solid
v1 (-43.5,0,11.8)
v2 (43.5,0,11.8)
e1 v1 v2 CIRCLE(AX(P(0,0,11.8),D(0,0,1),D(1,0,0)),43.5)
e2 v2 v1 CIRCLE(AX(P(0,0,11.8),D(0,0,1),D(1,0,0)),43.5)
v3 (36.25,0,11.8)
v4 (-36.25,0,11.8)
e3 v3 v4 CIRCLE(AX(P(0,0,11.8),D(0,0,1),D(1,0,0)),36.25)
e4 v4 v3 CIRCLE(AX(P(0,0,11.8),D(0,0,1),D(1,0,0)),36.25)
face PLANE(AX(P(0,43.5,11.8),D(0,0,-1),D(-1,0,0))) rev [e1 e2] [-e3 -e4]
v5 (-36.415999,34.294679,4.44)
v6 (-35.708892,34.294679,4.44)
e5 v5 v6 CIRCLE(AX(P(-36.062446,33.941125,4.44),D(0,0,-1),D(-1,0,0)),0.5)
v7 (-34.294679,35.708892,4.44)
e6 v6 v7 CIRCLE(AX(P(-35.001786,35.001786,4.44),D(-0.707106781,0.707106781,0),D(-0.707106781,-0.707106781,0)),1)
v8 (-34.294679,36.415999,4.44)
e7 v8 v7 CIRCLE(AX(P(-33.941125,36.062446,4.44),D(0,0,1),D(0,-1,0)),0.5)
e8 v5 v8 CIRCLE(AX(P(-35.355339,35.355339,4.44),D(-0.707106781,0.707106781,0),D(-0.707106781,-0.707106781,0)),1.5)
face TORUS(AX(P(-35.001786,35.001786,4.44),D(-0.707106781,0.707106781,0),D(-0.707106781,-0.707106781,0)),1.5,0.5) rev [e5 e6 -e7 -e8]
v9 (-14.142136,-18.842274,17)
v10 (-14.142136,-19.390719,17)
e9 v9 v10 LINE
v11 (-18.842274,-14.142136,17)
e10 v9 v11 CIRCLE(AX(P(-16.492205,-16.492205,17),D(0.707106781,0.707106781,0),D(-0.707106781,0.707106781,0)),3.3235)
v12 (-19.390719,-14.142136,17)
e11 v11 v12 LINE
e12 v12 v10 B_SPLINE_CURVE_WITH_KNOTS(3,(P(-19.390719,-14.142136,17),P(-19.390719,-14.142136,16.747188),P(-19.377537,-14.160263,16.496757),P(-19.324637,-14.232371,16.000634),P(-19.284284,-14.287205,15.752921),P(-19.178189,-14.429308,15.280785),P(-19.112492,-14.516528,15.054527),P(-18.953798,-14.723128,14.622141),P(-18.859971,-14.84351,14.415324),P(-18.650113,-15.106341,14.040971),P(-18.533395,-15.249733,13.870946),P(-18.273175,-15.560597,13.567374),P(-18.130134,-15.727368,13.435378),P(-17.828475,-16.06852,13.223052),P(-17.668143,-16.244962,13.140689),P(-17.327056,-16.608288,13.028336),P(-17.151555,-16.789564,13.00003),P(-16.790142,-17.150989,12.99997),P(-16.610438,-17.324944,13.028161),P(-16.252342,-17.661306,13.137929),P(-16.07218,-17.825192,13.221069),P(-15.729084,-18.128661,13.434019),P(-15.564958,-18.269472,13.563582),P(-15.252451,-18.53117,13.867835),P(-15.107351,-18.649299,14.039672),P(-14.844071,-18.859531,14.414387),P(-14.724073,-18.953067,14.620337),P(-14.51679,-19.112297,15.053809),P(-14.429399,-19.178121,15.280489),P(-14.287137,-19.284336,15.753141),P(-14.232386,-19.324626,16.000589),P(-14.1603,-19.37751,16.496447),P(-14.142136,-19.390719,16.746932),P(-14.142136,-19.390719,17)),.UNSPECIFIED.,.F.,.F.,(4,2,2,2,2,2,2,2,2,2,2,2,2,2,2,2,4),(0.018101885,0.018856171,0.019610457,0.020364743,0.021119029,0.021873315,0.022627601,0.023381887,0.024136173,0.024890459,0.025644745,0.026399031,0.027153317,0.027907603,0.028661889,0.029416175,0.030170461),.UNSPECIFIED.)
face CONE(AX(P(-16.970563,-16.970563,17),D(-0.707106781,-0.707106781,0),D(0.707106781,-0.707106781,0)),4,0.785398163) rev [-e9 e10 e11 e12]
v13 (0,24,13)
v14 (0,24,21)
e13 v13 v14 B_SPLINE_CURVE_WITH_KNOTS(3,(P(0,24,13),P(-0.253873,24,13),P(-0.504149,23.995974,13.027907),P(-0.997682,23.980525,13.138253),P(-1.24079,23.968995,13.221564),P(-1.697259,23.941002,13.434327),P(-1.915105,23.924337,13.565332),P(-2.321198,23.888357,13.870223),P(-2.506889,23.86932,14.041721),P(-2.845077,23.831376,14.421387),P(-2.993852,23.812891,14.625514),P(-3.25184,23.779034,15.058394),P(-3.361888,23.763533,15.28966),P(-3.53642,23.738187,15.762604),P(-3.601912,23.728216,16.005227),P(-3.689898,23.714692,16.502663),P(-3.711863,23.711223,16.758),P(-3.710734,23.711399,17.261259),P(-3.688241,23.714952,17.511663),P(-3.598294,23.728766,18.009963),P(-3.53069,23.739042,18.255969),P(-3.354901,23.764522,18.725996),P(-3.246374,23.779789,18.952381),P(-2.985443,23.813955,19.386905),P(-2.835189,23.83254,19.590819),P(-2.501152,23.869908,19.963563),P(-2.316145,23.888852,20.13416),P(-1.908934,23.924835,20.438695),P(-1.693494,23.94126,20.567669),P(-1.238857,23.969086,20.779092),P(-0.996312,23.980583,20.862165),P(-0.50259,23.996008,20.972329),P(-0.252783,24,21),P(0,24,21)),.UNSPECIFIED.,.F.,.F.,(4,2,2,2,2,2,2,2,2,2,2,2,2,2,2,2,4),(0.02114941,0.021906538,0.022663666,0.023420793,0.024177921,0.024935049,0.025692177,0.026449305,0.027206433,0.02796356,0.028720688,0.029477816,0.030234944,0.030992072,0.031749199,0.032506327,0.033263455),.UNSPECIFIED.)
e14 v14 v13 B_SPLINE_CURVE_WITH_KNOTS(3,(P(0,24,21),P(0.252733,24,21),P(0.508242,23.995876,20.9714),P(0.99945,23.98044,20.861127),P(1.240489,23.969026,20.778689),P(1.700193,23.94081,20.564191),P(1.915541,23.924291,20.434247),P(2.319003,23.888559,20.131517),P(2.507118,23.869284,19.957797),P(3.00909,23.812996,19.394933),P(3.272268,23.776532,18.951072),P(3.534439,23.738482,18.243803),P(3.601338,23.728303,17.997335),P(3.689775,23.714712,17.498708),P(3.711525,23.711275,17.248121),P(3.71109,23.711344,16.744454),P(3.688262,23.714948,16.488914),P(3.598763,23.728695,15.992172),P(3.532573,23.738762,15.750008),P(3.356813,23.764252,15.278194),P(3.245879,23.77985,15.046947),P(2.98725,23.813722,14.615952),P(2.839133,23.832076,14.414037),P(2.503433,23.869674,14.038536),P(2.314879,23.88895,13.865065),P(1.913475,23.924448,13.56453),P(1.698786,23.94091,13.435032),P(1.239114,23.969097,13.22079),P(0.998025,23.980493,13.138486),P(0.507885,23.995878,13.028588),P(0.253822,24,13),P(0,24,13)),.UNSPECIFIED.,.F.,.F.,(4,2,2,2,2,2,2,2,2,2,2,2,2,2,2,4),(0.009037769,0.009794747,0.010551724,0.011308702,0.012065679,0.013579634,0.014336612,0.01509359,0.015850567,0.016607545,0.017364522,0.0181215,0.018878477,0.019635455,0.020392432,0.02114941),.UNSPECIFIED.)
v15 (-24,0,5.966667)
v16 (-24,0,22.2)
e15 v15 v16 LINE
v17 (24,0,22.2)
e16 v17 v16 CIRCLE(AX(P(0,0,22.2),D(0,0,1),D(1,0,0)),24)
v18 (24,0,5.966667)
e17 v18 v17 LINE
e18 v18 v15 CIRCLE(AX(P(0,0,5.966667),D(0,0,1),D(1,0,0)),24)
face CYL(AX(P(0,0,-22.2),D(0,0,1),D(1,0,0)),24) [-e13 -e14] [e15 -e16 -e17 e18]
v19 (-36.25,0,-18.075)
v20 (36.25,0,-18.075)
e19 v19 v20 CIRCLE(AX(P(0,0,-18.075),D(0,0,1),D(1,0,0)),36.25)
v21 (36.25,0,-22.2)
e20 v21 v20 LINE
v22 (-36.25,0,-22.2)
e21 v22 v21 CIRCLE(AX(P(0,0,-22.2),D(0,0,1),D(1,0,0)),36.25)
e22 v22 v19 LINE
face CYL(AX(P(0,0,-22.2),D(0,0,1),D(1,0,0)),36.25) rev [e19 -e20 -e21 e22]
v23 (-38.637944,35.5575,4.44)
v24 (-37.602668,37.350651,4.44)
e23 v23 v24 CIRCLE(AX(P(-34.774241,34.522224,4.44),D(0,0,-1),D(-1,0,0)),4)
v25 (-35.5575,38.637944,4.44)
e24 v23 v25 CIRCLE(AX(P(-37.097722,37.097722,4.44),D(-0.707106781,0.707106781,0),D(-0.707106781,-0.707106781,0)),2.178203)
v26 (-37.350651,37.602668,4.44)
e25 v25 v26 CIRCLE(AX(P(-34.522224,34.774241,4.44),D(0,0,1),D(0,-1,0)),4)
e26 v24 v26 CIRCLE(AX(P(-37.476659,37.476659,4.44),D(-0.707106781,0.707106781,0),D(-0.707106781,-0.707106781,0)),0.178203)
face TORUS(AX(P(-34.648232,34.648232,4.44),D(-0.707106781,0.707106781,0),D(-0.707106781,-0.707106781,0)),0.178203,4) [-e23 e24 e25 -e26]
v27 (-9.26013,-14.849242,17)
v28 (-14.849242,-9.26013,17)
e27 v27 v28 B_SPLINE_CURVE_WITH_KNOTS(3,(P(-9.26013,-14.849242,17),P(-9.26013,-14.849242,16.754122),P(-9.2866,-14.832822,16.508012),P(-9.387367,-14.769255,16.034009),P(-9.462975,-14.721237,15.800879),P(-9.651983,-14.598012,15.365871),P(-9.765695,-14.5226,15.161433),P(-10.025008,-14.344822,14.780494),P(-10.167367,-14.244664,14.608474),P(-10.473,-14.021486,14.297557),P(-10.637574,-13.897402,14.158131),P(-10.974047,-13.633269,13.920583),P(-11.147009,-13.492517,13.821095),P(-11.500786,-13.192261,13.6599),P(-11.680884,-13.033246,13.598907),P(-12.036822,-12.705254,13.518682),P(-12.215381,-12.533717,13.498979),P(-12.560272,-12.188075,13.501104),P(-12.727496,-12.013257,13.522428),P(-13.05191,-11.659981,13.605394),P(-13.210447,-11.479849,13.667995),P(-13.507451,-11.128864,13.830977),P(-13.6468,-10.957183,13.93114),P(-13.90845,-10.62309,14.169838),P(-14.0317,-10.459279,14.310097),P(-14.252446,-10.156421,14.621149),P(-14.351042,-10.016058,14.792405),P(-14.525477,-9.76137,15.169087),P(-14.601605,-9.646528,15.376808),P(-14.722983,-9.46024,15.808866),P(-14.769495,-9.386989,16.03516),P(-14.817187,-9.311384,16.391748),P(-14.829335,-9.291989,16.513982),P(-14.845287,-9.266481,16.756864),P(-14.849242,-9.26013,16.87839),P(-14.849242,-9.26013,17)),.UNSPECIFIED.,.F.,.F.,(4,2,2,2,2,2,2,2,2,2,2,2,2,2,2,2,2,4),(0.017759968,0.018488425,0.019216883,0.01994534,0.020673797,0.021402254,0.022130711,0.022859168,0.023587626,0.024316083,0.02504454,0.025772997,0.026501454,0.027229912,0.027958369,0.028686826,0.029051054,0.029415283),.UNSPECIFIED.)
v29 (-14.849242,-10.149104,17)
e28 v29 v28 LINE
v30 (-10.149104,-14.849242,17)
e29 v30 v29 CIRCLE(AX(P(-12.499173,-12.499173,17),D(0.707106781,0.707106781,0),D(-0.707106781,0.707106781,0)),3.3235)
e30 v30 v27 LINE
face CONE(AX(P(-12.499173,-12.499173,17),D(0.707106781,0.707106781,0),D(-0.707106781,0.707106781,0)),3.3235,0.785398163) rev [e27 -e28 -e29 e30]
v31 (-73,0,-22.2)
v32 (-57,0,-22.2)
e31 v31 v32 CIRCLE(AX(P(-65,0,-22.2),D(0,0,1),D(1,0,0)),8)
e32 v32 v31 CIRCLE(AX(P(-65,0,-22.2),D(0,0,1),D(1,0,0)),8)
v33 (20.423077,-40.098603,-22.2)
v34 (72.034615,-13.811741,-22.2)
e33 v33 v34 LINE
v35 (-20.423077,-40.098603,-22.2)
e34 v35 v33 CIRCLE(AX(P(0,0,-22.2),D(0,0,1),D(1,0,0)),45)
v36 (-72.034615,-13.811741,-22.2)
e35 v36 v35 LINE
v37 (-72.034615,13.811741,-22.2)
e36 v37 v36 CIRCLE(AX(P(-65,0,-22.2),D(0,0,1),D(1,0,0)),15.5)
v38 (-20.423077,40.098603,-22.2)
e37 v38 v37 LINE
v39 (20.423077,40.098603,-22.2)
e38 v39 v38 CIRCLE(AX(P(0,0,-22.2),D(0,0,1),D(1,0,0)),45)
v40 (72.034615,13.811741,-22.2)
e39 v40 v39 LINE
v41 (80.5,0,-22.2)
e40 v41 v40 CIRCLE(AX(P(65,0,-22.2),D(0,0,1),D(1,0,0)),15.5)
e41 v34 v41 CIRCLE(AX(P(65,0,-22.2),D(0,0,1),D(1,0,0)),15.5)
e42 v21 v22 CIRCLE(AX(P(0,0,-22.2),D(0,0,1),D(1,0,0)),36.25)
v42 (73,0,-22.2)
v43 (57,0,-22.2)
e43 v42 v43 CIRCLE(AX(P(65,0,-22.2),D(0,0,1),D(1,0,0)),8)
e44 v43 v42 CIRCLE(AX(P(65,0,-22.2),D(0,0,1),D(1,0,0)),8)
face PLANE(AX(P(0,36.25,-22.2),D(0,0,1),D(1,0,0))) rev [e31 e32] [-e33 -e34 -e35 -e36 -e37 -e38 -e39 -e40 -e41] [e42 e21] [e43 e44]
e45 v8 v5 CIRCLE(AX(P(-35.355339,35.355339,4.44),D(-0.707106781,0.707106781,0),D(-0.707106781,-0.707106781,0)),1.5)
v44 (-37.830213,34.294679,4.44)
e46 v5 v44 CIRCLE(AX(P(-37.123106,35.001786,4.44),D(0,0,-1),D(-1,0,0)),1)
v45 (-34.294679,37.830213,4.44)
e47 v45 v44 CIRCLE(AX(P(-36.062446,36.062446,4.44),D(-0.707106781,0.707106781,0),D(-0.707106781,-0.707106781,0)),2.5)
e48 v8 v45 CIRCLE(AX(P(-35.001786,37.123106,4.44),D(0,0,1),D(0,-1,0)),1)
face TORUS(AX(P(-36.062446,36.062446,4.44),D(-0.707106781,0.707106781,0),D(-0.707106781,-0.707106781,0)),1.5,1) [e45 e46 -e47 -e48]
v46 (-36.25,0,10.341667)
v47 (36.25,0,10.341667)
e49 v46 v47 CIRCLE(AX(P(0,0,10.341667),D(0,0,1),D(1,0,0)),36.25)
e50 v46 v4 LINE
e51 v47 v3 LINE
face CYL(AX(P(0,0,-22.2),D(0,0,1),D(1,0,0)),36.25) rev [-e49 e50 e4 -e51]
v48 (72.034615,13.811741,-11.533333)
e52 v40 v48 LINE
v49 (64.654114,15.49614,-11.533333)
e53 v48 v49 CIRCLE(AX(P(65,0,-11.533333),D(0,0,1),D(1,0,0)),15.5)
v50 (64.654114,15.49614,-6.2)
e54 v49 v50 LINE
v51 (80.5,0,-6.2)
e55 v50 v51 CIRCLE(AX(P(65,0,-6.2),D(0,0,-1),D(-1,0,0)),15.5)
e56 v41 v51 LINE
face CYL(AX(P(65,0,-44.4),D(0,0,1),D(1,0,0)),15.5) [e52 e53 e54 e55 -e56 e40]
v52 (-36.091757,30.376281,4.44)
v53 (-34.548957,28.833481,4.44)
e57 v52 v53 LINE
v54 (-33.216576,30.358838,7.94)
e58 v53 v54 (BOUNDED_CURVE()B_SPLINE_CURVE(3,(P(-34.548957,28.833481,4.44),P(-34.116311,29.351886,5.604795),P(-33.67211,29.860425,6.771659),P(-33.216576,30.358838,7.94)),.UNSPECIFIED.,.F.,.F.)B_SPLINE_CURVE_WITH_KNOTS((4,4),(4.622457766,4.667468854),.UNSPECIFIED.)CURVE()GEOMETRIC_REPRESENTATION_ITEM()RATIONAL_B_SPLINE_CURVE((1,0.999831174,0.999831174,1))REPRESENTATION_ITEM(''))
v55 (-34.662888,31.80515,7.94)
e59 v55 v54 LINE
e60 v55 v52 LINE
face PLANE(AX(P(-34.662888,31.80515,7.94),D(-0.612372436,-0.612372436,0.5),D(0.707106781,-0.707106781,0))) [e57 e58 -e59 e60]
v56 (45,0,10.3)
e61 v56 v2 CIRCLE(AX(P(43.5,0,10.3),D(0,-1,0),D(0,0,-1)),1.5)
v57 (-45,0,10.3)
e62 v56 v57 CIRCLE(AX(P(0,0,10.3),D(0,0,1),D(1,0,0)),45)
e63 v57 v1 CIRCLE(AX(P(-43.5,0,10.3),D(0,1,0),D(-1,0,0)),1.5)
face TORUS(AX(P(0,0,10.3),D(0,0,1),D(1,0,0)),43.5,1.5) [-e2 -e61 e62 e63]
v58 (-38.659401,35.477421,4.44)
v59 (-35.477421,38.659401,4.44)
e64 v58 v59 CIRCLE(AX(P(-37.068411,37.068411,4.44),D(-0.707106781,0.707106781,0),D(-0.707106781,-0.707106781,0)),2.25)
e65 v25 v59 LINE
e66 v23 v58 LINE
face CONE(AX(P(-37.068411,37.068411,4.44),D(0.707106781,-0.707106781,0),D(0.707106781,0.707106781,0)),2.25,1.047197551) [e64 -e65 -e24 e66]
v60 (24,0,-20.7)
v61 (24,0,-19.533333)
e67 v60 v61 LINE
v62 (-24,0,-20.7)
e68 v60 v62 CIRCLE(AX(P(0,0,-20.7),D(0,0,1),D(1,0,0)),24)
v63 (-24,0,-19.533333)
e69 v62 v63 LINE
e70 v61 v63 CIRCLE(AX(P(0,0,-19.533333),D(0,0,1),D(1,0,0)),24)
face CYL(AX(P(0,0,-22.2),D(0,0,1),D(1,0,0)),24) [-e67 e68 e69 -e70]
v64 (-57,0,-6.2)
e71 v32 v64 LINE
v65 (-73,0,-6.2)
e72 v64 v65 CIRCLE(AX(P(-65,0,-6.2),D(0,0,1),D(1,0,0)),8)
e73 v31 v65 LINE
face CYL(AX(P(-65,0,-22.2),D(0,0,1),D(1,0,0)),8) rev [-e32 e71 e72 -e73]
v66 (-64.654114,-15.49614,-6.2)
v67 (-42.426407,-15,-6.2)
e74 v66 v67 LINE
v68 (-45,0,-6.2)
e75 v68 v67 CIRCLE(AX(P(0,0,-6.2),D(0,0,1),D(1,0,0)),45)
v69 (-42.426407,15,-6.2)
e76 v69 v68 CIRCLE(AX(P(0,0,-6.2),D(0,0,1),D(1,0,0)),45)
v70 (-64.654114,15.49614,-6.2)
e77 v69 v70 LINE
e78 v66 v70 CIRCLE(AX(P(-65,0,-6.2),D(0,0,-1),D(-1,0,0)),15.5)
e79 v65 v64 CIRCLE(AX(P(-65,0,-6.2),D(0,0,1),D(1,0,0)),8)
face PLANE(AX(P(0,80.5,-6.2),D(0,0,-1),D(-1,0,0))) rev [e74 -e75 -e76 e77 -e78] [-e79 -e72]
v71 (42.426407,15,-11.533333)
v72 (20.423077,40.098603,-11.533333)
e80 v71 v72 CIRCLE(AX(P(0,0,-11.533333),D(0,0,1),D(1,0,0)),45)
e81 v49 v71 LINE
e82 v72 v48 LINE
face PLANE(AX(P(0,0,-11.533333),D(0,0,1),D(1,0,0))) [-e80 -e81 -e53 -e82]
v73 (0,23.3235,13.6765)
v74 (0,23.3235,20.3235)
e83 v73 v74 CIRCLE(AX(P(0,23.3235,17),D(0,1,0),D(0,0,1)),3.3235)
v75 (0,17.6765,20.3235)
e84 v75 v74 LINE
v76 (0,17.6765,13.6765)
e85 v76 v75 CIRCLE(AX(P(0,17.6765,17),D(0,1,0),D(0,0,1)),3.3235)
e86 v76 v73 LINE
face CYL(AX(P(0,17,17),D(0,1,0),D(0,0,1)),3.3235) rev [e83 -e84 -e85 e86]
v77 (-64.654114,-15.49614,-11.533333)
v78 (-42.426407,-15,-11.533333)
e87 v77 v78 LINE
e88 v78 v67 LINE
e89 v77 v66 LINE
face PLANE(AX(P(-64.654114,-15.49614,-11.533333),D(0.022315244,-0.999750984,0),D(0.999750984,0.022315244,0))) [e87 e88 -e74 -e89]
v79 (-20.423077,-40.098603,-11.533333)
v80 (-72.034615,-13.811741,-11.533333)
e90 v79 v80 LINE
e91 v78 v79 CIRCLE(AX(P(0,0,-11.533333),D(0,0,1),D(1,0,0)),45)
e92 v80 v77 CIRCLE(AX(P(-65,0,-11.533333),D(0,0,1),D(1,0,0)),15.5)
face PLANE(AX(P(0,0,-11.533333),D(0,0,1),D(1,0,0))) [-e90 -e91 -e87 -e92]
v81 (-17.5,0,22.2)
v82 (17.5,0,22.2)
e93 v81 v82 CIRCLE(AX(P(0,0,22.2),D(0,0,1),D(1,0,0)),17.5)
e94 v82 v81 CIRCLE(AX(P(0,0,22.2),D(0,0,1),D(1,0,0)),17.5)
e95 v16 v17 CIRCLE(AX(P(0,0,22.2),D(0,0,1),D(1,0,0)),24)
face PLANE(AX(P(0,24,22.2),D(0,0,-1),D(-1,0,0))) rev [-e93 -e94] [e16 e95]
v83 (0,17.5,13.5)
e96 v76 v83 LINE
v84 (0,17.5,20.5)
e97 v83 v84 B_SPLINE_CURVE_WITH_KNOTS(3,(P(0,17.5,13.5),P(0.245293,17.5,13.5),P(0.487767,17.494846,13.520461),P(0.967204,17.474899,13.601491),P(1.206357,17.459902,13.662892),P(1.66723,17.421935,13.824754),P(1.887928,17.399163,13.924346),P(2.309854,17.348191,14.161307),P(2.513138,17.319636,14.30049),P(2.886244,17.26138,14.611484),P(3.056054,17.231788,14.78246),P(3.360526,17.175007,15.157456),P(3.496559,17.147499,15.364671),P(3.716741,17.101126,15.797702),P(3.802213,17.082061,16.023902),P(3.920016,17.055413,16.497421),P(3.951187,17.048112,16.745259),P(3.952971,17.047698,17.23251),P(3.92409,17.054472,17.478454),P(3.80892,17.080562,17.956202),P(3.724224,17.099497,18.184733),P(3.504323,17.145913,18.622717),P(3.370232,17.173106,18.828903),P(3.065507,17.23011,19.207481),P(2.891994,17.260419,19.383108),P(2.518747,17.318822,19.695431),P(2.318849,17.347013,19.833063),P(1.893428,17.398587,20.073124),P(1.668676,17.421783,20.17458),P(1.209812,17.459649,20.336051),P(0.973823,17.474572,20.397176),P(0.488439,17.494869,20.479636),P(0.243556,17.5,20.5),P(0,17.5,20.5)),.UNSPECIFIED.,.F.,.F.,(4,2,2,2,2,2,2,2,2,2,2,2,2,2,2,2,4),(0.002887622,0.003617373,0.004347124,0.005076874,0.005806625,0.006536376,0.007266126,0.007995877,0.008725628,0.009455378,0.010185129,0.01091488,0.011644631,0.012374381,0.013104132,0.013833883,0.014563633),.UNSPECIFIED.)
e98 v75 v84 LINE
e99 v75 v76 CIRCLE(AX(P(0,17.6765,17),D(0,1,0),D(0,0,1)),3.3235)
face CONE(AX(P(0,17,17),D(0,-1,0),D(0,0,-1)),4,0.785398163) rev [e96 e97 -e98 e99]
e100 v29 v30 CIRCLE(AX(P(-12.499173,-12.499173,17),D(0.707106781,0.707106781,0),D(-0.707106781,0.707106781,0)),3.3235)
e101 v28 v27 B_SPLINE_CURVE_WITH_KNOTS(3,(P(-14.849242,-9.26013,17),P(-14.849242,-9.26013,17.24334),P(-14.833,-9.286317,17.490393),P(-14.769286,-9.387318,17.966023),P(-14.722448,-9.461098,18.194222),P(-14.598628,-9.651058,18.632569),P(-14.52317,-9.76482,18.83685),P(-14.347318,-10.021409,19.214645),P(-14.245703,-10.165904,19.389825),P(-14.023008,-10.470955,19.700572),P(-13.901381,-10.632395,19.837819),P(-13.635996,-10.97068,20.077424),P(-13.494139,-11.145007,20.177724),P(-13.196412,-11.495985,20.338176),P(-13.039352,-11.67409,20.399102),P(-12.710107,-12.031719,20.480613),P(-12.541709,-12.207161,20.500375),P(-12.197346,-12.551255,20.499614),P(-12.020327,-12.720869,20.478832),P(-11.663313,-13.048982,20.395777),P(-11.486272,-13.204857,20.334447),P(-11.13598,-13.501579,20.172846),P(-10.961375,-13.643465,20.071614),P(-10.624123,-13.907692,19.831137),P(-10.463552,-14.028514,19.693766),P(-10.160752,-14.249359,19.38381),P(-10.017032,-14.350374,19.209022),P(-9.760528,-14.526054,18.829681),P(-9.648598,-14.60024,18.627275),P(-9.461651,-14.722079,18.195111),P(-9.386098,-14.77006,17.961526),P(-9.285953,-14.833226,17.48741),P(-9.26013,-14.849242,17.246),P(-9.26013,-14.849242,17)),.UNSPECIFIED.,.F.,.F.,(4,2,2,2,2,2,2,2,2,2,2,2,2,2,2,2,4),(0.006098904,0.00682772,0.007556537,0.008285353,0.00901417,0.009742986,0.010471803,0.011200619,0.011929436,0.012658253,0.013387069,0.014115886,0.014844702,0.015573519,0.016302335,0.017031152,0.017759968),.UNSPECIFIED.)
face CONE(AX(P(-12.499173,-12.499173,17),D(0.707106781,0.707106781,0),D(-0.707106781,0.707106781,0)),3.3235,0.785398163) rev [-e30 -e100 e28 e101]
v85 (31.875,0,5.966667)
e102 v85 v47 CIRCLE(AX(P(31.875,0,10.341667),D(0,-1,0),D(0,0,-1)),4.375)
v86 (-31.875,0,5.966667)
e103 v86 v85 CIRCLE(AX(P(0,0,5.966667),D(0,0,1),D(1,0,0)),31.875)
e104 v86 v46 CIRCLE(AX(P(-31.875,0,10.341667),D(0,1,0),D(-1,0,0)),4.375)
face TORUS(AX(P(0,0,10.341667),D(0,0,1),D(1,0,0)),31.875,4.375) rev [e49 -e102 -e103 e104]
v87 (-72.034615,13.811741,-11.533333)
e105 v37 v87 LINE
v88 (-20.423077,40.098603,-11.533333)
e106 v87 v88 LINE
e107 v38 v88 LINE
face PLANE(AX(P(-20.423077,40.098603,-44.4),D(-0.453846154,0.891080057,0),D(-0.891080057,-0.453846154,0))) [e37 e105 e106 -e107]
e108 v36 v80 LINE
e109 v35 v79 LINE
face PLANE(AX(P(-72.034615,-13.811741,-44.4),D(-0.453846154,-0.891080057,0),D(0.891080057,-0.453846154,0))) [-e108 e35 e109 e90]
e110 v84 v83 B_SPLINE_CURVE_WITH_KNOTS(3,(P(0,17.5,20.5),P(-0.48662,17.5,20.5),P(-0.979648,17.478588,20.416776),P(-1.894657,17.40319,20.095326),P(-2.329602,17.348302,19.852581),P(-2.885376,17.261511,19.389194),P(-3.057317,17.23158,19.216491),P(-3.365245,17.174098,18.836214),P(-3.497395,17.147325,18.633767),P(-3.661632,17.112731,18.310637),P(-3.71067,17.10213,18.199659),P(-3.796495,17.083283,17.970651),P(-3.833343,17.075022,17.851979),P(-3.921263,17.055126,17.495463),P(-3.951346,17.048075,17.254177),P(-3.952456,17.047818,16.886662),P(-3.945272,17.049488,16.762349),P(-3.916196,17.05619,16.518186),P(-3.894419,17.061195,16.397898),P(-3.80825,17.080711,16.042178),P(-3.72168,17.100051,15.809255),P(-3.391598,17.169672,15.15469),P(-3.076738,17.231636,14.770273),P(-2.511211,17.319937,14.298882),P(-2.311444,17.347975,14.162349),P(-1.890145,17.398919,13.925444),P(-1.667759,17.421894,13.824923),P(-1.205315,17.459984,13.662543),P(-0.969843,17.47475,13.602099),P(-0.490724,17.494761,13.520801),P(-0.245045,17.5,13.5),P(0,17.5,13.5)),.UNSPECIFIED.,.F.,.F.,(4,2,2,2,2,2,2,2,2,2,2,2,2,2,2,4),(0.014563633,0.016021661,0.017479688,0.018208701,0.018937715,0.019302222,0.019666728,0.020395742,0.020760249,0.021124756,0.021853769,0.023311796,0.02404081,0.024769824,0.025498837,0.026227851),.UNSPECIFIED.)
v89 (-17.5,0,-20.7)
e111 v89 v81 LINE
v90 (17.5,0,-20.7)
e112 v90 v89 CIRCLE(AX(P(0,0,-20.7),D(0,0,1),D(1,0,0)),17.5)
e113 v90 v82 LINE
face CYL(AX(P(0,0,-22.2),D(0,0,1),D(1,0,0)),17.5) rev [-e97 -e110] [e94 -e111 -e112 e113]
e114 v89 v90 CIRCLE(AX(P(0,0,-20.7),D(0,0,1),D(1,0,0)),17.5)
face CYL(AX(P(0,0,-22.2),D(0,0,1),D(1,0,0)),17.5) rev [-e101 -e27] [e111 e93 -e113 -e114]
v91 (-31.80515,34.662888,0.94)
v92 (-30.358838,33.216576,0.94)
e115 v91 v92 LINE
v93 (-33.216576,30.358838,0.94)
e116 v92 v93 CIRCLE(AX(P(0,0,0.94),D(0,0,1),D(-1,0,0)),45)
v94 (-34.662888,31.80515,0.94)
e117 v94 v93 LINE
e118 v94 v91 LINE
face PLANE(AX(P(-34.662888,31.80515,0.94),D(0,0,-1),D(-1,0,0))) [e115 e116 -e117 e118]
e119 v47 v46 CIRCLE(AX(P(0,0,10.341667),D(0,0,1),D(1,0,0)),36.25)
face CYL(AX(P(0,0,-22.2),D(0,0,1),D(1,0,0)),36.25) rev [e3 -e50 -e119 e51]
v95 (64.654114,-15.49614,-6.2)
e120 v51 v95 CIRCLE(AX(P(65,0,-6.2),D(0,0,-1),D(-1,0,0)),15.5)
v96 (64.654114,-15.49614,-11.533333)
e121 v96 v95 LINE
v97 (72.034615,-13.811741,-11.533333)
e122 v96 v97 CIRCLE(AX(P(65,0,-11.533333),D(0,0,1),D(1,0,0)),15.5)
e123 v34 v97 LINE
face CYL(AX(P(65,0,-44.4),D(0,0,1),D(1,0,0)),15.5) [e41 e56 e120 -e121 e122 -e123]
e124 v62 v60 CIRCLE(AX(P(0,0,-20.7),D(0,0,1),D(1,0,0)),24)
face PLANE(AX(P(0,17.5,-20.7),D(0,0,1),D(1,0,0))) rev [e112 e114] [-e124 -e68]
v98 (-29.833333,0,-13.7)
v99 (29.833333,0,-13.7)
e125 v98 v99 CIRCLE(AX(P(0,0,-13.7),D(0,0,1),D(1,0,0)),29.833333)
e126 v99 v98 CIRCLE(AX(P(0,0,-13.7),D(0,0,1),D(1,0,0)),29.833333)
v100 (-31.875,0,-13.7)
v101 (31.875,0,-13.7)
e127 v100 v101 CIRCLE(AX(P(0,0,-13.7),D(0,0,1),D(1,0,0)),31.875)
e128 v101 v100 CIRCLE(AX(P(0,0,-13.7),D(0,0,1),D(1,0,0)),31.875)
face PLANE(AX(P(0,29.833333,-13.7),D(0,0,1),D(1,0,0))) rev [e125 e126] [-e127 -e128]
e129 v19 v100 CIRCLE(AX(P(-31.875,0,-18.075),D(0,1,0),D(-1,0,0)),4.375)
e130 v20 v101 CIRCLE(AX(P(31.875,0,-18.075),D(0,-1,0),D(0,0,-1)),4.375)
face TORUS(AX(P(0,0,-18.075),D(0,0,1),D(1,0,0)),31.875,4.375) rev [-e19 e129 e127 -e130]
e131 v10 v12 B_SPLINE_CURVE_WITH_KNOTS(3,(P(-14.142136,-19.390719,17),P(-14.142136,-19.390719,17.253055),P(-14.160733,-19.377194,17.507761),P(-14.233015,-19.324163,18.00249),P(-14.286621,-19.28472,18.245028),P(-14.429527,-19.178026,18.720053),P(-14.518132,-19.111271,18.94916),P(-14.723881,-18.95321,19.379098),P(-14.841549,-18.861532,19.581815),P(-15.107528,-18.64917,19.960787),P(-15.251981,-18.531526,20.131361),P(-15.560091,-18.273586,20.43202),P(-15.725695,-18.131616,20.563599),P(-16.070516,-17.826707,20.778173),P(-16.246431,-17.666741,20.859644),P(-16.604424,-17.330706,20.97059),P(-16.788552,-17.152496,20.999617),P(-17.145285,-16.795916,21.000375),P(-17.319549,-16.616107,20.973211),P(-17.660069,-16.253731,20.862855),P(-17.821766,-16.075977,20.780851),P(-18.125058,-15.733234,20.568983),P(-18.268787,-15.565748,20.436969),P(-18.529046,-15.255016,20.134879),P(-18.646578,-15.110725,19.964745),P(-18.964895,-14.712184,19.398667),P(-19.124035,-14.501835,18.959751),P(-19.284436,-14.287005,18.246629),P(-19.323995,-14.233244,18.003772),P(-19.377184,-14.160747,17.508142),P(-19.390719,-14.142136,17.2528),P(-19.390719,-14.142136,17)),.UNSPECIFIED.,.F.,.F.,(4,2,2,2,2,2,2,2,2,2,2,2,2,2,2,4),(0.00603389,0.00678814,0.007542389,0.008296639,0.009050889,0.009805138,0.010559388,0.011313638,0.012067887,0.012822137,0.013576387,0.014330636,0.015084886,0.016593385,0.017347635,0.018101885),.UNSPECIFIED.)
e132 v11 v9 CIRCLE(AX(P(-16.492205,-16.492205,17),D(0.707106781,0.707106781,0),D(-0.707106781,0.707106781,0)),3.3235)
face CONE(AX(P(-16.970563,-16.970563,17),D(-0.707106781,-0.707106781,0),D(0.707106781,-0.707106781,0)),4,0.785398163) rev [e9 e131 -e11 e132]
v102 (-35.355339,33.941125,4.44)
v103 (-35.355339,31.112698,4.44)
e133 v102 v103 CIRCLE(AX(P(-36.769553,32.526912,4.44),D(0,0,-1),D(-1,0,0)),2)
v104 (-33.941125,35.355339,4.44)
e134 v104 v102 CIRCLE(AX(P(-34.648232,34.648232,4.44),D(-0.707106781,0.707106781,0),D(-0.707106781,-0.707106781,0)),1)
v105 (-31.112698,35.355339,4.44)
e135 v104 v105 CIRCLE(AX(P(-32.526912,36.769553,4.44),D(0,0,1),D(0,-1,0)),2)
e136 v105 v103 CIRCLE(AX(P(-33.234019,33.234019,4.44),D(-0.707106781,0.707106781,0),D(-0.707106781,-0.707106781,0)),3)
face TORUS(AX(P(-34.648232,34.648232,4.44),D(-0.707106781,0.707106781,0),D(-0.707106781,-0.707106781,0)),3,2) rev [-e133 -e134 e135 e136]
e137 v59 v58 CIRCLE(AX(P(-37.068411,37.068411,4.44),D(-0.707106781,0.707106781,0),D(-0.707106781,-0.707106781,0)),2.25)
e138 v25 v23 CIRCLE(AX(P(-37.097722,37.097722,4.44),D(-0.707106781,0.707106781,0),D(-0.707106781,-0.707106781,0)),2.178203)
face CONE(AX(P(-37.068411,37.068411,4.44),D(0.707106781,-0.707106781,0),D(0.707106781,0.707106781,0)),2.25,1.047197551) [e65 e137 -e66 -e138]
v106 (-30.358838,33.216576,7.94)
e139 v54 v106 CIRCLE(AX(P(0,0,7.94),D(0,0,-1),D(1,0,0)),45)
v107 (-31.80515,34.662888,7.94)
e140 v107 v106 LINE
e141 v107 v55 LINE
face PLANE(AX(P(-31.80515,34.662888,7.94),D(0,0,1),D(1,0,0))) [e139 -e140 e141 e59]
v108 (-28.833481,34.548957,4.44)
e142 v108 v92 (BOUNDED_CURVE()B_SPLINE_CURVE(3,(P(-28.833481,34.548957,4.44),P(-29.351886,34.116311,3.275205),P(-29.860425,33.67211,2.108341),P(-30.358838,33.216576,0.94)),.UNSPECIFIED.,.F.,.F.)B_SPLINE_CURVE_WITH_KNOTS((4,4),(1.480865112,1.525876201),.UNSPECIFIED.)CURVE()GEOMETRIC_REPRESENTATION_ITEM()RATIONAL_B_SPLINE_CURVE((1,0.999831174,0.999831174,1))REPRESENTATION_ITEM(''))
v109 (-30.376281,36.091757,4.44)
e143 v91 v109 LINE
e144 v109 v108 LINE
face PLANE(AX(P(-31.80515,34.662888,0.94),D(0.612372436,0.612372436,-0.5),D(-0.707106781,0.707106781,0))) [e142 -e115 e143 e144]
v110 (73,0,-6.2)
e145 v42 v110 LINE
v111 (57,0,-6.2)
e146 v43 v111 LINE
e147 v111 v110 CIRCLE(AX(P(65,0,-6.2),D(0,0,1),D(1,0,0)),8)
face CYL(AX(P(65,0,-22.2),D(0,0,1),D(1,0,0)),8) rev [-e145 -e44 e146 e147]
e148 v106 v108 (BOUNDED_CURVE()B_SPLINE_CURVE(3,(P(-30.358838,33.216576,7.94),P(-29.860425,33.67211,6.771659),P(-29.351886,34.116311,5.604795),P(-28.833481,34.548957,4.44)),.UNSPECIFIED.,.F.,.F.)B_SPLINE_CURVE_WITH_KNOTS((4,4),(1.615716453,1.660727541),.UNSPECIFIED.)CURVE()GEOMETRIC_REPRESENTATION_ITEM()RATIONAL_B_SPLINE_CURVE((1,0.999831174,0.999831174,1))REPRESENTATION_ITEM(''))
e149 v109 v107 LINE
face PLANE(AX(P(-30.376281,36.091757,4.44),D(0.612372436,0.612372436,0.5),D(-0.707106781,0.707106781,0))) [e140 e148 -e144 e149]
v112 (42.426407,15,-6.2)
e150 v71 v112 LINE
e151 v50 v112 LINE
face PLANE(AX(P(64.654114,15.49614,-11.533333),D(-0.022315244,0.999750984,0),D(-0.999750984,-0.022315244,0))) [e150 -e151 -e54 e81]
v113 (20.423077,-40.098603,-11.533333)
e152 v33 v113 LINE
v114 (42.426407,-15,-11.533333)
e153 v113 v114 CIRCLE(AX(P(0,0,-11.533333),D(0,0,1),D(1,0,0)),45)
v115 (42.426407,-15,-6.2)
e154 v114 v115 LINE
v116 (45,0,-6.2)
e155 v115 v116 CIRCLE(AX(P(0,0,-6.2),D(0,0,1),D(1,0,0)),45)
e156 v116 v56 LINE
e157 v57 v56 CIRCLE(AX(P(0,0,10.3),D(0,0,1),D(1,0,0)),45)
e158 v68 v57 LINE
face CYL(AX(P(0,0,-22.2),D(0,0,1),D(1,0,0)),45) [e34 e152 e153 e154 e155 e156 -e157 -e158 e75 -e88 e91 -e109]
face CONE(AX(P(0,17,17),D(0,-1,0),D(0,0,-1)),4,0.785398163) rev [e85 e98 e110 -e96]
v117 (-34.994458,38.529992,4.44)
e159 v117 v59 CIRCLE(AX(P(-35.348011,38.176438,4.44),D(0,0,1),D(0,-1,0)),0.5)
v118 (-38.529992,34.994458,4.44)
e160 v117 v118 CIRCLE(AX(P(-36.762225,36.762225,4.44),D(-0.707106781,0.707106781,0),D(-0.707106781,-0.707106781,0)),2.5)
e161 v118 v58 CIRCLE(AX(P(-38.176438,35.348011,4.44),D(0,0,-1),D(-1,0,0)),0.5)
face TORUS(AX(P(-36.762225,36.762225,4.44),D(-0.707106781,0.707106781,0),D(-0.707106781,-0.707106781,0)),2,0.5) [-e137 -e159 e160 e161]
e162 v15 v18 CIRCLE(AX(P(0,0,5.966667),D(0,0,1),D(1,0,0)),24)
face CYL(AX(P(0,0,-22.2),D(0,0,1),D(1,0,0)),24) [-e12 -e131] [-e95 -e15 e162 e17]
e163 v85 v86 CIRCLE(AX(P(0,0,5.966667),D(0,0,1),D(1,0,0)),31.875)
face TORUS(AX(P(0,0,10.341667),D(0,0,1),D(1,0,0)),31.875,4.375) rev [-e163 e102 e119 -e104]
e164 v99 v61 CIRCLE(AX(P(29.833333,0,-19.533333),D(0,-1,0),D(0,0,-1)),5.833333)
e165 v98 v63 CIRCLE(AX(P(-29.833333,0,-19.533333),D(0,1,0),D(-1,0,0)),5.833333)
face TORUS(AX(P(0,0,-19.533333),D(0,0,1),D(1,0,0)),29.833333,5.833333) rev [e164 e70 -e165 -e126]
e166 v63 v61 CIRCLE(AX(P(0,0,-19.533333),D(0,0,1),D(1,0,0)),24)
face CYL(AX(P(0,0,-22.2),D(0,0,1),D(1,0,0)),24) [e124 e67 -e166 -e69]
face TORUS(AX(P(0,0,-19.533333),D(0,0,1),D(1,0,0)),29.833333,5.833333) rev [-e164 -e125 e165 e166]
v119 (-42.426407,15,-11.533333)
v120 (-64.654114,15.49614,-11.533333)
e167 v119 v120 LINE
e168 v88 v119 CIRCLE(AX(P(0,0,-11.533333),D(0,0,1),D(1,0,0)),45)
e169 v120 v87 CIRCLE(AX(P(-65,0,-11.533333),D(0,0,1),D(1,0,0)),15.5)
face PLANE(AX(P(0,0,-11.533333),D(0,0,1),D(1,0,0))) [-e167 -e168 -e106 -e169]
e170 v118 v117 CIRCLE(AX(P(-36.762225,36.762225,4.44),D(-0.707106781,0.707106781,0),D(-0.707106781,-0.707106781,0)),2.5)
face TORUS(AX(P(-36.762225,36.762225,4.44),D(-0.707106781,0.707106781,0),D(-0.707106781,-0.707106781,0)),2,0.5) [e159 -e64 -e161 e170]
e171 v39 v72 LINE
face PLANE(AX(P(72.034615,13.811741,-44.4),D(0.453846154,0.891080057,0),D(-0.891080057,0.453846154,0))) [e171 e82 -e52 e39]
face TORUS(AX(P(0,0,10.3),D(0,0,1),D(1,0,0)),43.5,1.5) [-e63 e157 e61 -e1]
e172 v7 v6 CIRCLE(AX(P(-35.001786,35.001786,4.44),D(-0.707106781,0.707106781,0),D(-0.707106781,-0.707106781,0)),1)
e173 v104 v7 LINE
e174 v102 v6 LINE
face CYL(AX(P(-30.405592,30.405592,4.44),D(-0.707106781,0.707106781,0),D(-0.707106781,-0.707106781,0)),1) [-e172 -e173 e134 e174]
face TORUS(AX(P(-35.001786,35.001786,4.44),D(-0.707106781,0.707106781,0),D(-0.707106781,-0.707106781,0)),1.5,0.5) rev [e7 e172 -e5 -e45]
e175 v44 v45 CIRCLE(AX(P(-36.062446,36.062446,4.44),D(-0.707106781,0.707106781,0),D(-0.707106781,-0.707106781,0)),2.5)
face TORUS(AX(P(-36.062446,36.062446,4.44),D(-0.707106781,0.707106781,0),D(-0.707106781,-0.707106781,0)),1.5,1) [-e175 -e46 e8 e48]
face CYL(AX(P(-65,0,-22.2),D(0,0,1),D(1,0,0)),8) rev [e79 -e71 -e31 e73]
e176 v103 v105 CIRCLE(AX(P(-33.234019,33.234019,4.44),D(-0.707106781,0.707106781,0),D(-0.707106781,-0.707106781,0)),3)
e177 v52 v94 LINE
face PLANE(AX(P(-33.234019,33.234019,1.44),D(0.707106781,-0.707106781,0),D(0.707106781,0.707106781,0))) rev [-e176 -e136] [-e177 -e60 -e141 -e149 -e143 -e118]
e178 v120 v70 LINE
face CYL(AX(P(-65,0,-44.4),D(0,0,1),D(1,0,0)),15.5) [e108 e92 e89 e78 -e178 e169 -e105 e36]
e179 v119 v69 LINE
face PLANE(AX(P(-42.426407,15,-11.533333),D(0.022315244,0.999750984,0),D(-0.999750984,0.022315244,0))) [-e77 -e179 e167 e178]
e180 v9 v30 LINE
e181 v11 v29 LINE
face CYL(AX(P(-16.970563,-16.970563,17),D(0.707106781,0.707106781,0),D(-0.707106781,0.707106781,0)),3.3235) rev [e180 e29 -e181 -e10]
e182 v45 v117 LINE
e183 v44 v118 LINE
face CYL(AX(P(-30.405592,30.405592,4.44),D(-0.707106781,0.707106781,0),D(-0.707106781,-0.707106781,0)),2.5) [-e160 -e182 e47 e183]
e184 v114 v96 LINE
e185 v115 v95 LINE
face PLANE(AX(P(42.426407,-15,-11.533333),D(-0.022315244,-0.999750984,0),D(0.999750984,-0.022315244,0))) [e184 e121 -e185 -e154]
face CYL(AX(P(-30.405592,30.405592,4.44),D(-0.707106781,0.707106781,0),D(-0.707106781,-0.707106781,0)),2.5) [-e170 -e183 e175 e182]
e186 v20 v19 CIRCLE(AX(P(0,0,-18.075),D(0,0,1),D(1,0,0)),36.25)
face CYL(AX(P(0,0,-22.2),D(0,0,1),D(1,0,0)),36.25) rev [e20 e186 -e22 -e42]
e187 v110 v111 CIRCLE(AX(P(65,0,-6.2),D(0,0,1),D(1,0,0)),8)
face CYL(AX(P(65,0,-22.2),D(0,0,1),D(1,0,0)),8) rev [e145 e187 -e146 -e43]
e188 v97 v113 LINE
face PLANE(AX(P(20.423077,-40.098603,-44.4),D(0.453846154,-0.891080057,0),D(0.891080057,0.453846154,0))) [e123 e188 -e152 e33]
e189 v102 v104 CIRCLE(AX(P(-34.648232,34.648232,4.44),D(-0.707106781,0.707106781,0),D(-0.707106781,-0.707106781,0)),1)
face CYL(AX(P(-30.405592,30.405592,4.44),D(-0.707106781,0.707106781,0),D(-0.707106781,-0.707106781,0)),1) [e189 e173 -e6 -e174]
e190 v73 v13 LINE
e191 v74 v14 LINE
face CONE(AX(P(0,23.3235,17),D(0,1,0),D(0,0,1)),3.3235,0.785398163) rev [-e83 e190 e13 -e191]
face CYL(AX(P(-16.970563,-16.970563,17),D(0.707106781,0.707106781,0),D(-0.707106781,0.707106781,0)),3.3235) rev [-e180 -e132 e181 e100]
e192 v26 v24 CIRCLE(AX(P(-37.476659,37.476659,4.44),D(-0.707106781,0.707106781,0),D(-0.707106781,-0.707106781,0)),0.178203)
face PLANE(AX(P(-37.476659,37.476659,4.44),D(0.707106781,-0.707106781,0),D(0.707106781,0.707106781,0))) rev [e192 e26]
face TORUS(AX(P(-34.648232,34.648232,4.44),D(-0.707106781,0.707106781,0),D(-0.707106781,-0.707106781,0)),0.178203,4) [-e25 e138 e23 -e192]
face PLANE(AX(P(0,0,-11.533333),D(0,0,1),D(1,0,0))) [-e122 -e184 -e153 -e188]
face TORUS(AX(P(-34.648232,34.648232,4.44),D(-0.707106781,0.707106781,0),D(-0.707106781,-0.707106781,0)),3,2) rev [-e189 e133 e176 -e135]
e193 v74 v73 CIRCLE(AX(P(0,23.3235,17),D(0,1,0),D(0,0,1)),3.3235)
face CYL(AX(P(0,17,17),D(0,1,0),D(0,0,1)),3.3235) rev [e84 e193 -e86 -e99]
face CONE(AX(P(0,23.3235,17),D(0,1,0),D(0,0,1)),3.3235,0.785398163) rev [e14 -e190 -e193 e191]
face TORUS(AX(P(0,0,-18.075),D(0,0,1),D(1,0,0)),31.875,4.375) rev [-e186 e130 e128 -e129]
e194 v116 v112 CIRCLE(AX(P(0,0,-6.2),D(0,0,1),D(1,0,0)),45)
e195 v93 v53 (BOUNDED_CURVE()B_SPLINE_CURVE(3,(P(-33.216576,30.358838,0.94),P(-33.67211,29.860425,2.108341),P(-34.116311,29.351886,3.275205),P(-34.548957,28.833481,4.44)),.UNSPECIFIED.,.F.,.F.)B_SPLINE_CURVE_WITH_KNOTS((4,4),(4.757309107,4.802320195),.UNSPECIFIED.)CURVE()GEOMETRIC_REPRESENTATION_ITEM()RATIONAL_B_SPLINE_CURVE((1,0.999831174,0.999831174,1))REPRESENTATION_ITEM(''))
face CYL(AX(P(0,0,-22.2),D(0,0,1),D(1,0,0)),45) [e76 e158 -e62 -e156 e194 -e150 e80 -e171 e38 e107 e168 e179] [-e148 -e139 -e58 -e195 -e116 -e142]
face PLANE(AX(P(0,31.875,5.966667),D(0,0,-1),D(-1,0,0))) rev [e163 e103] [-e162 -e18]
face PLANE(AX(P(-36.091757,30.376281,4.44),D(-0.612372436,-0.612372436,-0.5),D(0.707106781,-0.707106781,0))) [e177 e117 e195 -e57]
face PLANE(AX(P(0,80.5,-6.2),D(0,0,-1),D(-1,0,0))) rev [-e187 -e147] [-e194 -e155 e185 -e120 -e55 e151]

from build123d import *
from build123d.topology import SkipClean

# Parameters (mm, degrees)
SKETCH2_W          = 10.260420585
SKETCH2_H          = 10.310228453
CUT_EXTRUDE1_DEPTH = 4
SKETCH4_W          = 468
SKETCH4_H          = 360
CUT_EXTRUDE2_DEPTH = 44.4
SKETCH5_W          = 234
SKETCH5_H          = 180
CUT_EXTRUDE3_DEPTH = 5.333333333
SKETCH6_R          = 8
CUT_EXTRUDE4_DEPTH = 16
SKETCH7_R          = 8
CUT_EXTRUDE5_DEPTH = 16


with BuildPart() as part:
    # Sketch1 → Revolve1 (revolve)
    with BuildSketch(Plane(origin=(0, 0, 0), x_dir=(0, 0, -1), z_dir=(0.7071067811865476, 0.7071067811865475, 0)), mode=Mode.PRIVATE) as revolve1_sk:
        with BuildLine():
            Line((-4.44, 53), (-4.26179677, 53))
            ThreePointArc((-4.26179677, 53), (-3.226520589, 52.863703305), (-2.26179677, 52.464101615))
            Line((-2.26179677, 52.464101615), (-2.19, 52.422649731))
            ThreePointArc((-2.19, 52.422649731), (-2.006987298, 52.239637029), (-1.94, 51.989637029))
            Line((-1.94, 51.989637029), (-1.94, 51))
            ThreePointArc((-1.94, 51), (-2.232893219, 50.292893219), (-2.94, 50))
            ThreePointArc((-2.94, 50), (-3.293553391, 49.853553391), (-3.44, 49.5))
            Line((-3.44, 49.5), (-3.44, 49))
            ThreePointArc((-3.44, 49), (-2.854213562, 47.585786438), (-1.44, 47))
            Line((-1.44, 47), (0.56, 47))
            Line((0.56, 47), (0.56, 43))
            Line((0.56, 43), (-4.44, 43))
            Line((-4.44, 43), (-4.44, 53))
        make_face()
    revolve(revolve1_sk.sketch.rotate(Axis((-30.405591591, 30.405591591, 4.44), (-0.7071067811865477, 0.7071067811865474, 0)), 90), axis=Axis((-30.405591591, 30.405591591, 4.44), (-0.7071067811865477, 0.7071067811865474, 0)))

    # Sketch2 → Cut-Extrude1 (cut)
    with BuildSketch(Plane(origin=(-30.405591591, 30.405591591, 0), x_dir=(0, 0, -1), z_dir=(0.7071067811865501, -0.7071067811865449, 0))):
        with Locations((-4.564519667, -0.074711801)):
            Rectangle(SKETCH2_W, SKETCH2_H)
        Polygon((-7.94, 2.020725942), (-7.94, -2.020725942), (-4.44, -4.041451884), (-0.94, -2.020725942), (-0.94, 2.020725942), (-4.44, 4.041451884), align=None, mode=Mode.SUBTRACT)
    extrude(amount=-CUT_EXTRUDE1_DEPTH, mode=Mode.SUBTRACT)

    # Sketch3 → Revolve2 (revolve)
    with BuildSketch(Plane(origin=(0, 0, 0), x_dir=(0, 0, -1), z_dir=(1, 0, 0)), mode=Mode.PRIVATE) as revolve2_sk:
        with BuildLine():
            Line((-22.2, 24), (-22.2, 17.5))
            Line((-22.2, 17.5), (20.7, 17.5))
            Line((20.7, 17.5), (20.7, 24))
            Line((20.7, 24), (19.533333333, 24))
            ThreePointArc((19.533333333, 24), (15.408543776, 25.708543776), (13.7, 29.833333333))
            Line((13.7, 29.833333333), (13.7, 31.875))
            ThreePointArc((13.7, 31.875), (14.981407832, 34.968592168), (18.075, 36.25))
            Line((18.075, 36.25), (22.2, 36.25))
            Line((22.2, 36.25), (22.2, 80.5))
            Line((22.2, 80.5), (6.2, 80.5))
            Line((6.2, 80.5), (6.2, 45))
            Line((6.2, 45), (-10.3, 45))
            ThreePointArc((-10.3, 45), (-11.360660172, 44.560660172), (-11.8, 43.5))
            Line((-11.8, 43.5), (-11.8, 36.25))
            Line((-11.8, 36.25), (-10.341666667, 36.25))
            ThreePointArc((-10.341666667, 36.25), (-7.248074499, 34.968592168), (-5.966666667, 31.875))
            Line((-5.966666667, 31.875), (-5.966666667, 24))
            Line((-5.966666667, 24), (-22.2, 24))
        make_face()
    revolve(revolve2_sk.sketch.rotate(Axis((0, 0, -22.2), (0, 0, 1)), 270), axis=Axis((0, 0, -22.2), (0, 0, 1)))

    # Sketch4 → Cut-Extrude2 (cut)
    with SkipClean():  # the faces are left unmerged after this step: merging them gives an invalid solid
        with BuildSketch(Plane.XY):
            Rectangle(SKETCH4_W, SKETCH4_H)
            with BuildLine():
                Line((-72.034615385, -13.811740889), (-20.423076923, -40.098602582))
                ThreePointArc((-20.423076923, -40.098602582), (0, -45), (20.423076923, -40.098602582))
                Line((20.423076923, -40.098602582), (72.034615385, -13.811740889))
                ThreePointArc((72.034615385, -13.811740889), (80.5, 0), (72.034615385, 13.811740889))
                Line((72.034615385, 13.811740889), (20.423076923, 40.098602582))
                ThreePointArc((20.423076923, 40.098602582), (0, 45), (-20.423076923, 40.098602582))
                Line((-20.423076923, 40.098602582), (-72.034615385, 13.811740889))
                ThreePointArc((-72.034615385, 13.811740889), (-80.5, 0), (-72.034615385, -13.811740889))
            make_face(mode=Mode.SUBTRACT)
        extrude(amount=-CUT_EXTRUDE2_DEPTH, mode=Mode.SUBTRACT)

    # Sketch5 → Cut-Extrude3 (cut)
    with SkipClean():  # the faces are left unmerged after this step: merging them gives an invalid solid
        with BuildSketch(Plane.XY.offset(-6.2)):
            Rectangle(SKETCH5_W, SKETCH5_H)
            with BuildLine():
                Line((-64.654113716, -15.496140251), (-42.426406871, -15))
                ThreePointArc((-42.426406871, -15), (0, -45), (42.426406871, -15))
                Line((42.426406871, -15), (64.654113716, -15.496140251))
                ThreePointArc((64.654113716, -15.496140251), (80.5, 0), (64.654113716, 15.496140251))
                Line((64.654113716, 15.496140251), (42.426406871, 15))
                ThreePointArc((42.426406871, 15), (0, 45), (-42.426406871, 15))
                Line((-42.426406871, 15), (-64.654113716, 15.496140251))
                ThreePointArc((-64.654113716, 15.496140251), (-80.5, 0), (-64.654113716, -15.496140251))
            make_face(mode=Mode.SUBTRACT)
        extrude(amount=-CUT_EXTRUDE3_DEPTH, mode=Mode.SUBTRACT)

    # Sketch6 → Cut-Extrude4 (cut)
    with SkipClean():  # the faces are left unmerged after this step: merging them gives an invalid solid
        with BuildSketch(Plane.XY.offset(-6.2)):
            with Locations((-65, 0)):
                Circle(SKETCH6_R)
        extrude(amount=-CUT_EXTRUDE4_DEPTH, mode=Mode.SUBTRACT)

    # Sketch7 → Cut-Extrude5 (cut)
    with SkipClean():  # the faces are left unmerged after this step: merging them gives an invalid solid
        with BuildSketch(Plane.XY.offset(-6.2)):
            with Locations((65, 0)):
                Circle(SKETCH7_R)
        extrude(amount=-CUT_EXTRUDE5_DEPTH, mode=Mode.SUBTRACT)

    # Sketch8 → Cut-Revolve1 (revolve, cut)
    with SkipClean():  # the faces are left unmerged after this step: merging them gives an invalid solid
        with BuildSketch(Plane(origin=(0, 0, 0), x_dir=(0, 0, -1), z_dir=(1, 0, 0)), mode=Mode.PRIVATE) as cut_revolve1_sk:
            Polygon((-17, 24), (-13, 24), (-13.6765, 23.3235), (-13.6765, 17.6765), (-13, 17), (-17, 17), align=None)
        revolve(cut_revolve1_sk.sketch.rotate(Axis((0, 17, 17), (0, 1, 0)), 180), axis=Axis((0, 17, 17), (0, 1, 0)), mode=Mode.SUBTRACT)

    # Sketch9 → Cut-Revolve2 (revolve, cut)
    with SkipClean():  # the faces are left unmerged after this step: merging them gives an invalid solid
        with BuildSketch(Plane(origin=(0, 0, 0), x_dir=(0, 0, -1), z_dir=(0.7071067811865476, -0.7071067811865475, 0)), mode=Mode.PRIVATE) as cut_revolve2_sk:
            Polygon((-17, -17), (-13, -17), (-13.6765, -17.6765), (-13.6765, -23.3235), (-13, -24), (-17, -24), align=None)
        revolve(cut_revolve2_sk.sketch.rotate(Axis((-16.970562748, -16.970562748, 17), (0.7071067811865476, 0.7071067811865476, 0)), 90), axis=Axis((-16.970562748, -16.970562748, 17), (0.7071067811865476, 0.7071067811865476, 0)), mode=Mode.SUBTRACT)


solid = part.part
